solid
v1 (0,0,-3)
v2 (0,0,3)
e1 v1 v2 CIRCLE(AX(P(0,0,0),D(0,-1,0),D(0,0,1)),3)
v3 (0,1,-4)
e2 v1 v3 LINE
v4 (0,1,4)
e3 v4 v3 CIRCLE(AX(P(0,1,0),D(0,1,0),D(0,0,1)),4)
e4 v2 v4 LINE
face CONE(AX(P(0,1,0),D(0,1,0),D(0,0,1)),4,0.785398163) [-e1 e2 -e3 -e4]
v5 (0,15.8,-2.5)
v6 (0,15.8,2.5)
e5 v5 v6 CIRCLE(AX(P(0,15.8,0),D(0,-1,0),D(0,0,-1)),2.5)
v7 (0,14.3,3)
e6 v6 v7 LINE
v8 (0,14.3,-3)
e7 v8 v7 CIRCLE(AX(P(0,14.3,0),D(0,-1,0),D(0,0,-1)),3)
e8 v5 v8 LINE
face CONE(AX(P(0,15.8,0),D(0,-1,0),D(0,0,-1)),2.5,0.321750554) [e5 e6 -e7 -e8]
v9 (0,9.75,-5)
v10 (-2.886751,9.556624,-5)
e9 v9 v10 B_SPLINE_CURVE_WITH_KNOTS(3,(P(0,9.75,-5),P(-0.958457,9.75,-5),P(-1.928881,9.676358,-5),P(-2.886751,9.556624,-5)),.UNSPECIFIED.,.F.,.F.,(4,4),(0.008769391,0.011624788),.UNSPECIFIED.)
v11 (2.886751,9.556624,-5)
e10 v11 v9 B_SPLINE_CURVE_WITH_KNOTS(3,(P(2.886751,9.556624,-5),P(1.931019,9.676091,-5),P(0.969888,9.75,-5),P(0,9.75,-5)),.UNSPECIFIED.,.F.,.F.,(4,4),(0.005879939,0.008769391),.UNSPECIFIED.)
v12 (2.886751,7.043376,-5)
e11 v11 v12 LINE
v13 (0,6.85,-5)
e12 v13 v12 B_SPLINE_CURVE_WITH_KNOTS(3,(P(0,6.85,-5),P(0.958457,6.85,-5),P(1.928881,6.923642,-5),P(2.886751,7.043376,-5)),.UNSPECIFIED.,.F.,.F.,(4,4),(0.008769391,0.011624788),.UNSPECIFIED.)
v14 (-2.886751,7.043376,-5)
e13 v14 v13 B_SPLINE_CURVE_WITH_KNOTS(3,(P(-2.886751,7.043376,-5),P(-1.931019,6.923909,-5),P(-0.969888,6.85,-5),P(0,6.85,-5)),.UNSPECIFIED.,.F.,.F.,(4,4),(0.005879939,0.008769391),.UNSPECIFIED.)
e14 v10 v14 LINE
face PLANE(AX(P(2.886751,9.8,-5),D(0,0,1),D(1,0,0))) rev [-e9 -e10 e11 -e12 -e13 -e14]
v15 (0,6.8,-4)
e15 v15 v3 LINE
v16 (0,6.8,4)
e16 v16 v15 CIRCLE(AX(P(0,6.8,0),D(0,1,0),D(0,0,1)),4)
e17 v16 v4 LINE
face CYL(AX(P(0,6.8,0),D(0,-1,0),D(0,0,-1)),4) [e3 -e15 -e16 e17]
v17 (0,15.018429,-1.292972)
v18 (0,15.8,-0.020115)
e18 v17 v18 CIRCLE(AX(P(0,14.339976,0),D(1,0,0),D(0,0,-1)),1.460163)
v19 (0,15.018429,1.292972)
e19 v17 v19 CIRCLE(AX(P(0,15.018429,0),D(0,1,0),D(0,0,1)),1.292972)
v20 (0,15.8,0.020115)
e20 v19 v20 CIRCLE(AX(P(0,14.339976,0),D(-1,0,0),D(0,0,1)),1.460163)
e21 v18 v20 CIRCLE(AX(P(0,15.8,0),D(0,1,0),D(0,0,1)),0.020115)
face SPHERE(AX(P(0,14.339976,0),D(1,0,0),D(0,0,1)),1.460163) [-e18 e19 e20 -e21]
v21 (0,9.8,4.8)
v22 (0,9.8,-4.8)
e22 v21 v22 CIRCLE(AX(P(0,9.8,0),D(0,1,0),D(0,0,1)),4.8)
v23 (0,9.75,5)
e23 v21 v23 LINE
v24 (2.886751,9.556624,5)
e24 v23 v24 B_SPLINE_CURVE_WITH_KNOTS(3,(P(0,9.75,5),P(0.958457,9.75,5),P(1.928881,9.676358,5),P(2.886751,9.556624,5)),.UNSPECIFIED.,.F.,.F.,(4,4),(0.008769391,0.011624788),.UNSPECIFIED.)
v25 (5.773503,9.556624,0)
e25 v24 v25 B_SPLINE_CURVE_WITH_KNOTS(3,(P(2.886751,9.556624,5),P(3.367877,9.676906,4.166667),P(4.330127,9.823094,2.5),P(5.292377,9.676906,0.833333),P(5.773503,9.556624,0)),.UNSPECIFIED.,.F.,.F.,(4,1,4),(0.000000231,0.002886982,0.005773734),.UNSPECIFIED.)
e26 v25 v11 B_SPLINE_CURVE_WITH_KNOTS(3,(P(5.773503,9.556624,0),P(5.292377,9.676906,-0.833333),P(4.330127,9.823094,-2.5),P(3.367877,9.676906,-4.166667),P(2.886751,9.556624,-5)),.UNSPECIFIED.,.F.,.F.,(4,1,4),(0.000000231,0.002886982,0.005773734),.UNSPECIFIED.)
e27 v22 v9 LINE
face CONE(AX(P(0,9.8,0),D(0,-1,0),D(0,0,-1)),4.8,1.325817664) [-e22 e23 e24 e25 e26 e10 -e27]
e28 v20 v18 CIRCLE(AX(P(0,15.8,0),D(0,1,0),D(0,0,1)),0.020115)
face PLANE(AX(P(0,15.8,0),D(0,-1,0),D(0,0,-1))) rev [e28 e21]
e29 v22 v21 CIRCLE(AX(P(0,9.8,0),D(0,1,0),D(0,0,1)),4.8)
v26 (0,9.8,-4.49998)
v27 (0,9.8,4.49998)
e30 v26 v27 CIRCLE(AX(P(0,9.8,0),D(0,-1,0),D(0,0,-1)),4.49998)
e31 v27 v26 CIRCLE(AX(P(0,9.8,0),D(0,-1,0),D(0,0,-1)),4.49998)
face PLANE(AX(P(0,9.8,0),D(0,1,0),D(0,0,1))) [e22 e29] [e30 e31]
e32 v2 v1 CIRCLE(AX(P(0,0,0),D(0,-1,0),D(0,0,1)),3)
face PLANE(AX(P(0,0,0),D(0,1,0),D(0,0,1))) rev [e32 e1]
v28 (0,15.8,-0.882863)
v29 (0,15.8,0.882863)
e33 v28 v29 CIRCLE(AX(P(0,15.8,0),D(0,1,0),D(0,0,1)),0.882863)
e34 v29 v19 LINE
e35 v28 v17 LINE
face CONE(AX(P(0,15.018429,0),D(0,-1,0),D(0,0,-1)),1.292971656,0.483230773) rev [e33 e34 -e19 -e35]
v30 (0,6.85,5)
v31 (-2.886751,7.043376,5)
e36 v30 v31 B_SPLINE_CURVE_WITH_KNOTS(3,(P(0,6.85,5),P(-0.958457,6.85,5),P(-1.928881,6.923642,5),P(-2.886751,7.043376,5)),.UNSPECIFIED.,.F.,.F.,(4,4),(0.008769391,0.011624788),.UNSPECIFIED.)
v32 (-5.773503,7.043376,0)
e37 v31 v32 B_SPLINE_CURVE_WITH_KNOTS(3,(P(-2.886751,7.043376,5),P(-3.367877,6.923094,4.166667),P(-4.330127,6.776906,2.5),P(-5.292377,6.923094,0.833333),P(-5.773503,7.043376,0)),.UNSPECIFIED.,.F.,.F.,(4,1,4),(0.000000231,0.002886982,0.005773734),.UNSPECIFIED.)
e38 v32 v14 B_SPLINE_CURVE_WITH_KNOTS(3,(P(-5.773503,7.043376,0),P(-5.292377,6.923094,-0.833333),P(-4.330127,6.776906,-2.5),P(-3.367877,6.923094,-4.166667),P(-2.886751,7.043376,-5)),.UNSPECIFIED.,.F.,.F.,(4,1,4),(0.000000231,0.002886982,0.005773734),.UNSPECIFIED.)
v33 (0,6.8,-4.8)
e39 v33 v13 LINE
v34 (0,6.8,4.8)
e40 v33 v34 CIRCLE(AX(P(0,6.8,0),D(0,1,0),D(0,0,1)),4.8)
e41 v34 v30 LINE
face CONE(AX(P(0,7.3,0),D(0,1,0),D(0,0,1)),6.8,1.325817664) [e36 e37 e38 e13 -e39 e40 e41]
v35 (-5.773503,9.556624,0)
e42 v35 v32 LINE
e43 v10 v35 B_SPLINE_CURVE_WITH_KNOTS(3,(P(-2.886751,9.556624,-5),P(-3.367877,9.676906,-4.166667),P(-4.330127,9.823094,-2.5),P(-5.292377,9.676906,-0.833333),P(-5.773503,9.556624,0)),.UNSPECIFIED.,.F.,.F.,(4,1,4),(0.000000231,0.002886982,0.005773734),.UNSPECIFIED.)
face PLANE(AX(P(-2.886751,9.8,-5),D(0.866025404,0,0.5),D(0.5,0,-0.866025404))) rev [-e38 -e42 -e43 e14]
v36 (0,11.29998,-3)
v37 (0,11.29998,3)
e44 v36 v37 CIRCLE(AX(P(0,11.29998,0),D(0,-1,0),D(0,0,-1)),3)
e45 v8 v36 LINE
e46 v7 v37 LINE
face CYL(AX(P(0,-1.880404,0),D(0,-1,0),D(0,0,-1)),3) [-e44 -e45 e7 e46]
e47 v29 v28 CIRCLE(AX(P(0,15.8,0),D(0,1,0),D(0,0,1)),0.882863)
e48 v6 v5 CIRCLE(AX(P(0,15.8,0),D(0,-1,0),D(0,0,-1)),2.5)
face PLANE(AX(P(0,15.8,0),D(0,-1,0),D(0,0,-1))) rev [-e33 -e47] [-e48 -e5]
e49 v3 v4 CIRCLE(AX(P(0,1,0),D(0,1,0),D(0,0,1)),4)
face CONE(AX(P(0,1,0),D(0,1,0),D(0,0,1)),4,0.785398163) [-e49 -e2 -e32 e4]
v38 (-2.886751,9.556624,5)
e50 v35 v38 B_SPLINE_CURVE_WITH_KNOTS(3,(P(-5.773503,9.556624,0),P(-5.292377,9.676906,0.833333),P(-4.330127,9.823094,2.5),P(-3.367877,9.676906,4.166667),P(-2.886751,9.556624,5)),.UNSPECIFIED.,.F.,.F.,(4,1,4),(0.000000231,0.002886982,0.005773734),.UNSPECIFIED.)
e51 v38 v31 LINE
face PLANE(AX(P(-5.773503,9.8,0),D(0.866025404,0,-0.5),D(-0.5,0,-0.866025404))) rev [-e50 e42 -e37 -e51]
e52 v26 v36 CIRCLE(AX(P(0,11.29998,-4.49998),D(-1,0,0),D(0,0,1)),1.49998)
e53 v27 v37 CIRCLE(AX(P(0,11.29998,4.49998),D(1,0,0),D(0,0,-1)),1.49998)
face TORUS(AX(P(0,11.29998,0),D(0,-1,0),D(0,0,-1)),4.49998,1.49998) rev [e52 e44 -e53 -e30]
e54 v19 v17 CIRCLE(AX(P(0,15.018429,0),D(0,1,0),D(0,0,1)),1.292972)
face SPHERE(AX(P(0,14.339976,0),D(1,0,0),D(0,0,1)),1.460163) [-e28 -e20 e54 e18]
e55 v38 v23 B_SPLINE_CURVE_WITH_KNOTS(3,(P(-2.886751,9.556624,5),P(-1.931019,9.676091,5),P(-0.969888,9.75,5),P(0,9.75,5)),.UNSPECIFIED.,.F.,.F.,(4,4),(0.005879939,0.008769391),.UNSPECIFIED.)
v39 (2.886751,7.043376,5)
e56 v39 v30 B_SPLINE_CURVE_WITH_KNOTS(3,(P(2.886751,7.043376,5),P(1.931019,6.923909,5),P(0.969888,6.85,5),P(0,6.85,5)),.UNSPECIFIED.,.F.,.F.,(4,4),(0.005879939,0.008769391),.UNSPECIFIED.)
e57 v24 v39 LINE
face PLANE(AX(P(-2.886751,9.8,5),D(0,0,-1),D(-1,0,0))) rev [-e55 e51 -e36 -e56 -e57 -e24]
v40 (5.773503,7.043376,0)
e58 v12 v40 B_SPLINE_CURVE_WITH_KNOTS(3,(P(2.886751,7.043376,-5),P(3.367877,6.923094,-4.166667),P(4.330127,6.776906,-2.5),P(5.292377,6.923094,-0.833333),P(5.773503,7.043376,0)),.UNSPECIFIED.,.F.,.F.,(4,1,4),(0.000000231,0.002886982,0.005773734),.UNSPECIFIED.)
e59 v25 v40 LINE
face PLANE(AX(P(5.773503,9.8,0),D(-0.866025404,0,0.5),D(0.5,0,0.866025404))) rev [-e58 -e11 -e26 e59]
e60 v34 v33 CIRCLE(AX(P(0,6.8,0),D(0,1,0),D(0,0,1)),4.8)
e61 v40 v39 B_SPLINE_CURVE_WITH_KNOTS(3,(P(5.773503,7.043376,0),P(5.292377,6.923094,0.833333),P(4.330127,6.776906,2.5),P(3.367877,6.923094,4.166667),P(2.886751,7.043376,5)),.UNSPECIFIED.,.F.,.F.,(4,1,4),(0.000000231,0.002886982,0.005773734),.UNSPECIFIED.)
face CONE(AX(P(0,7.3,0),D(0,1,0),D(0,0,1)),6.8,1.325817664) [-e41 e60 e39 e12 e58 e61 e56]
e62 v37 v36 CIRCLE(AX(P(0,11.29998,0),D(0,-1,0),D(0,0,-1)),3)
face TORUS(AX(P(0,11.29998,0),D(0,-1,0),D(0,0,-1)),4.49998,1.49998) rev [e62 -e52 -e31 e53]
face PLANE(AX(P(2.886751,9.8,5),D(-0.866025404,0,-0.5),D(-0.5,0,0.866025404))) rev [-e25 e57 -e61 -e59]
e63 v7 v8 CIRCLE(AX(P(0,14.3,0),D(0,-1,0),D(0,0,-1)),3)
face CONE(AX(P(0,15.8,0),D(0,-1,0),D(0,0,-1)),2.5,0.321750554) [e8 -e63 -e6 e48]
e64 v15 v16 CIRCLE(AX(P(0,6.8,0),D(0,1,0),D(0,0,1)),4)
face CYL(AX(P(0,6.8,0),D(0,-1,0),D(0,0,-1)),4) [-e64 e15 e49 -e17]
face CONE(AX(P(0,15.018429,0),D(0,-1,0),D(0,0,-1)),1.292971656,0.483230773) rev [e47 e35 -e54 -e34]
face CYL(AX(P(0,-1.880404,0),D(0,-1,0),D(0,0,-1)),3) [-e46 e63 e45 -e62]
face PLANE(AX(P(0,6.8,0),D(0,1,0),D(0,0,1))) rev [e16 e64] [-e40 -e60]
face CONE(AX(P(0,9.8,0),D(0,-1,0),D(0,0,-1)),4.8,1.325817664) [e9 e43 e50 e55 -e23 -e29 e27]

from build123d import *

# Parameters (mm, degrees)
SKETCH1_R           = 4
BOSS_EXTRUDE1_DEPTH = 6.8
BOSS_EXTRUDE2_DEPTH = 3
CHAMFER1_SIZE       = 1


with BuildPart() as part:
    # Sketch1 → Boss-Extrude1 (new body)
    with BuildSketch(Plane(origin=(0, 0, 0), x_dir=(1, 0, 0), z_dir=(0, 1, 0))):
        with Locations(Location((0, 0, 0), (0, 0, 270))):
            Circle(SKETCH1_R)
    extrude(amount=BOSS_EXTRUDE1_DEPTH)

    # Sketch2 → Boss-Extrude2 (add)
    with BuildSketch(Plane(origin=(0, 6.8, 0), x_dir=(1, 0, 0), z_dir=(0, 1, 0))):
        Polygon((2.886751346, -5), (5.773502692, 0), (2.886751346, 5), (-2.886751346, 5), (-5.773502692, 0), (-2.886751346, -5), align=None)
    extrude(amount=BOSS_EXTRUDE2_DEPTH)

    # Sketch3 → Revolve1 (revolve)
    with BuildSketch(Plane.XY, mode=Mode.PRIVATE) as revolve1_sk:
        with BuildLine():
            Line((0, 15.8), (0, 9.8))
            Line((0, 9.8), (4.500264384, 9.8))
            ThreePointArc((4.500264384, 9.8), (3.439434496, 10.239233666), (3, 11.29998038))
            Line((3, 11.29998038), (3, 14.3))
            Line((3, 14.3), (2.5, 15.8))
            Line((2.5, 15.8), (0, 15.8))
        make_face()
    revolve(revolve1_sk.sketch.rotate(Axis((0, -1.880404244, 0), (0, 1, 0)), 90), axis=Axis((0, -1.880404244, 0), (0, 1, 0)))

    # Sketch5 → Cut-Revolve1 (revolve, cut)
    with BuildSketch(Plane(origin=(0, 0, 0), x_dir=(0, 0, -1), z_dir=(1, 0, 0)), mode=Mode.PRIVATE) as cut_revolve1_sk:
        Polygon((-6.8, 9.8), (-4.8, 9.8), (-6.8, 9.3), align=None)
        Polygon((-6.8, 7.3), (-4.8, 6.8), (-6.8, 6.8), align=None)
    revolve(cut_revolve1_sk.sketch.rotate(Axis((0, 16.999618754, 0), (0, -1, 0)), 209.999999988), axis=Axis((0, 16.999618754, 0), (0, -1, 0)), mode=Mode.SUBTRACT)

    # Chamfer1
    chamfer1_edges = [part.edges().sort_by_distance(p)[0] for p in [
        (0, 0, -4),
    ]]
    chamfer(chamfer1_edges, length=CHAMFER1_SIZE)

    # Sketch6 → Cut-Revolve4 (revolve, cut)
    with BuildSketch(Plane(origin=(0, 0, 0), x_dir=(0, 0, -1), z_dir=(1, 0, 0))):
        with BuildLine():
            ThreePointArc((-1.292971656, 15.018429463), (-0.764043535, 15.584287943), (-0.02011539, 15.8))
            Line((-0.02011539, 15.8), (-0.882862678, 15.8))
            Line((-0.882862678, 15.8), (-1.292971656, 15.018429463))
        make_face()
    revolve(axis=Axis((0, 16.917153181, 0), (0, -1, 0)), mode=Mode.SUBTRACT)


solid = part.part
